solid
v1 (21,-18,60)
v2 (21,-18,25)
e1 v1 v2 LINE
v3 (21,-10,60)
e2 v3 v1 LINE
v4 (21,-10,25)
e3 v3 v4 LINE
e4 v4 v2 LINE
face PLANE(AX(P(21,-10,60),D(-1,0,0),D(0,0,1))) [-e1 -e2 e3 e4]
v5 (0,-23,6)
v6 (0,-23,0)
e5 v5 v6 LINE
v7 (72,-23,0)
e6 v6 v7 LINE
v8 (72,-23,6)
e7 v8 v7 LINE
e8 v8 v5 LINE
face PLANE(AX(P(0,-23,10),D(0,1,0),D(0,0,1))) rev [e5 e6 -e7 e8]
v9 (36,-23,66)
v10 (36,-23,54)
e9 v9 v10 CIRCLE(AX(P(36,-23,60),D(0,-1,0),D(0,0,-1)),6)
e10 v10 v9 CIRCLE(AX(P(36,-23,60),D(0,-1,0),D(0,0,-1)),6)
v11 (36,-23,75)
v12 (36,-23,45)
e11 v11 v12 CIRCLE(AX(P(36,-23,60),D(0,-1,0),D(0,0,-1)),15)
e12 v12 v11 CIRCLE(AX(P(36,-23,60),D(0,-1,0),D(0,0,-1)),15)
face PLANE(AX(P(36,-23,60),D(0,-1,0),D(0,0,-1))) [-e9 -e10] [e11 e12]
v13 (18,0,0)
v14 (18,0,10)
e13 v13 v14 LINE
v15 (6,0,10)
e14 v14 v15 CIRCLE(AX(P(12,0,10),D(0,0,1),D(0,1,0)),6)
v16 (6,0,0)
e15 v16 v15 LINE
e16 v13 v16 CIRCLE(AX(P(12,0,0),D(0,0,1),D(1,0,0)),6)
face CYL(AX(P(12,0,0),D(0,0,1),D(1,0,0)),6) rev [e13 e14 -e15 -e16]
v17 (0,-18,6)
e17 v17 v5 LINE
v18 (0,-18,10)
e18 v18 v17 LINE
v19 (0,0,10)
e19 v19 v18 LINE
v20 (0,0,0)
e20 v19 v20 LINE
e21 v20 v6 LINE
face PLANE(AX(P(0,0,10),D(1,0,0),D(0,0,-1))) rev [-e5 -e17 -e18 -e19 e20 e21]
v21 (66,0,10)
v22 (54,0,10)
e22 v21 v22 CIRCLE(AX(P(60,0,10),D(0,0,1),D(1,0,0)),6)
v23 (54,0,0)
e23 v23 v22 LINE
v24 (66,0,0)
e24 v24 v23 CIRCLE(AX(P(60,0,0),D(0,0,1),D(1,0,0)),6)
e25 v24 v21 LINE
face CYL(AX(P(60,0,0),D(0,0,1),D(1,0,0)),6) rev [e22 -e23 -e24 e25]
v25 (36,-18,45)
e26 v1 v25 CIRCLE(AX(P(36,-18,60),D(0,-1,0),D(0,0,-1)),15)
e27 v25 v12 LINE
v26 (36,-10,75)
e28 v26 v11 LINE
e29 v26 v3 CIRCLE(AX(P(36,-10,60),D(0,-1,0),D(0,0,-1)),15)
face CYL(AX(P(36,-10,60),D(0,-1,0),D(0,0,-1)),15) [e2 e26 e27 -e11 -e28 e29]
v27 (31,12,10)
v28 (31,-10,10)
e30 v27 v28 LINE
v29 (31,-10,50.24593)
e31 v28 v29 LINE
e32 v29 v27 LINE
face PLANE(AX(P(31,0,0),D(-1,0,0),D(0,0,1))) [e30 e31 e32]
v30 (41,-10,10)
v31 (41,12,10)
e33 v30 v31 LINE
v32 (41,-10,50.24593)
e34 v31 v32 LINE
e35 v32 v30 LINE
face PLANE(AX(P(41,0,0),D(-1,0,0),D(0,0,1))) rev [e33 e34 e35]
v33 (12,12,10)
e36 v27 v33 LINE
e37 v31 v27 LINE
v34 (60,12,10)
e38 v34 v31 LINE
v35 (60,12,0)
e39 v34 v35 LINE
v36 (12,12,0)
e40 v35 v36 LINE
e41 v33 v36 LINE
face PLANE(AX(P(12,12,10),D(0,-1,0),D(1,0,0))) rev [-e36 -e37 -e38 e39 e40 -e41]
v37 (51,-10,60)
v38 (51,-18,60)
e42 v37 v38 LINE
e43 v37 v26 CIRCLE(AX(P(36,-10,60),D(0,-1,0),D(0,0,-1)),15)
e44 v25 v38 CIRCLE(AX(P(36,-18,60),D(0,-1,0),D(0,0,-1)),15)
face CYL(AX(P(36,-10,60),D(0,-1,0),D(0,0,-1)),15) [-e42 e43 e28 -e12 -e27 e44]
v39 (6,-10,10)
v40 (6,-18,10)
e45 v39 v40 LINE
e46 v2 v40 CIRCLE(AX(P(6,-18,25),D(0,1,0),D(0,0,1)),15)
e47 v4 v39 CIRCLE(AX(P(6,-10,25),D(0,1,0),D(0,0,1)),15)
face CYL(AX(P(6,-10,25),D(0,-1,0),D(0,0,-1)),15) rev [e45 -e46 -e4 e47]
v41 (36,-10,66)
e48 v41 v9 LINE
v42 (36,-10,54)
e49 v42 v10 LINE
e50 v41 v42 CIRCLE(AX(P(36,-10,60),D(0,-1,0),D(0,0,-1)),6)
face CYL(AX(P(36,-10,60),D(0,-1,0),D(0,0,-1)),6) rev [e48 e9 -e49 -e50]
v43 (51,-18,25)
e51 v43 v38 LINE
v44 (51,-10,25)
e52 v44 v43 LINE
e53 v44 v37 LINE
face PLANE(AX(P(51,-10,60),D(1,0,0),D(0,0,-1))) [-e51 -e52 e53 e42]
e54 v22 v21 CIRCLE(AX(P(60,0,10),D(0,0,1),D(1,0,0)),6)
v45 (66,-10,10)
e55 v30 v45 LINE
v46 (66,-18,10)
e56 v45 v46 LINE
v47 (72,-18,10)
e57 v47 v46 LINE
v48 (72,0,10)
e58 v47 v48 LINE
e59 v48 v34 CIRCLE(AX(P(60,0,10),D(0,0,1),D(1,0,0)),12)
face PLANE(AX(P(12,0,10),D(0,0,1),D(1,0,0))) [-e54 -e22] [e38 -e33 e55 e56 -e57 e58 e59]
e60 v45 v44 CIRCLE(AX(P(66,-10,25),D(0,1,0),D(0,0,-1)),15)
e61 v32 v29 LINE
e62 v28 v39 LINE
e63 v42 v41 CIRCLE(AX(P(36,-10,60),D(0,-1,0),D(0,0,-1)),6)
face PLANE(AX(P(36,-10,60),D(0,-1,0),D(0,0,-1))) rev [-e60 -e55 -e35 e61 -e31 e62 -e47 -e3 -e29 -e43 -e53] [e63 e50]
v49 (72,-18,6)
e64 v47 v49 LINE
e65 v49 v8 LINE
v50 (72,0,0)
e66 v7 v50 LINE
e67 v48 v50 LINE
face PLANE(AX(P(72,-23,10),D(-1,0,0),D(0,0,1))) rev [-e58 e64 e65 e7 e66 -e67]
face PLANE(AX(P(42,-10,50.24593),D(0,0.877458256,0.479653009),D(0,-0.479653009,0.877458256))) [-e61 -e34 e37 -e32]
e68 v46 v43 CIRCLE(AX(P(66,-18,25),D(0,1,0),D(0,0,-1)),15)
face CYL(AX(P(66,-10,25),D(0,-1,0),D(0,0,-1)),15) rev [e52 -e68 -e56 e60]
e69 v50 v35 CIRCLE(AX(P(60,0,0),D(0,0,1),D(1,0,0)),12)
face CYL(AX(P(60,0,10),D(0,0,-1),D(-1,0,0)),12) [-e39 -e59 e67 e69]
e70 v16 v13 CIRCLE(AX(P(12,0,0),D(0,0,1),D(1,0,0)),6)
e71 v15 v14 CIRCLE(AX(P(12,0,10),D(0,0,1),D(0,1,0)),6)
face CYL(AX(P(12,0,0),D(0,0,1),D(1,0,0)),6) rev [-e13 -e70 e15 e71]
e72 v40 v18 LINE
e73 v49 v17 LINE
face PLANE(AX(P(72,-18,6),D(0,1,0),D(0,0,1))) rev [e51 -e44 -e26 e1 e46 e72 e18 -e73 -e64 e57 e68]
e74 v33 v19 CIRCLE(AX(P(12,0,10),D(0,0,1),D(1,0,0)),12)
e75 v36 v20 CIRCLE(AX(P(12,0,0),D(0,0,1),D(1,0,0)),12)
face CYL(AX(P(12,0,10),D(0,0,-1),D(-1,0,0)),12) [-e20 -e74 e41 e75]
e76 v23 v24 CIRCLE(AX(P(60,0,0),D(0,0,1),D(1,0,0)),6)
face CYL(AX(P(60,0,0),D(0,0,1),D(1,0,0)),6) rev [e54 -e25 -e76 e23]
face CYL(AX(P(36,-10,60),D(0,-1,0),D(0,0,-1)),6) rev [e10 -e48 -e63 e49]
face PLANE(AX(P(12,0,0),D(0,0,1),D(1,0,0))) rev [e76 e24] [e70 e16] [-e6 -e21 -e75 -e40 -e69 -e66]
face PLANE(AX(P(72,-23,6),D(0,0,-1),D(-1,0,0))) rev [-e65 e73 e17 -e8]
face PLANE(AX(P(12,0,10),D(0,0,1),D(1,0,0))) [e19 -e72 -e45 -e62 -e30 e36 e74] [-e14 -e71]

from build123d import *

# Parameters (mm, degrees)
MOUNTING_PLATE_DEPTH     = 10
PLATE_NOTCH_SKETCH_W     = 4
PLATE_NOTCH_SKETCH_H     = 5
PLATE_NOTCH_CUT_DEPTH    = 72
PIVOT_ARM_DEPTH          = 8
PIVOT_START              = 5
PIVOT_BOSS_SKETCH_R      = 15
PIVOT_BOSS_30_DEPTH      = 5
PLATE_HOLES_SKETCH_R     = 6
PLATE_HOLES_2X_12_DEPTH  = 10
PIVOT_HOLE_SKETCH_R      = 6
PIVOT_HOLE_12_DEPTH      = 13
GUSSET_BLANK_DEPTH       = 42
GUSSET_TAPER_CUT_DEPTH   = 30
GUSSET_EDGE_TRIM_A_DEPTH = 1
GUSSET_EDGE_TRIM_B_DEPTH = 1


with BuildPart() as part:
    # Plate Profile Sketch → Mounting Plate (new body)
    with BuildSketch(Plane.XY):
        with BuildLine():
            Line((0, 0), (0, -23))
            Line((0, -23), (72, -23))
            Line((72, -23), (72, 0))
            ThreePointArc((72, 0), (68.485281374, 8.485281374), (60, 12))
            Line((60, 12), (12, 12))
            ThreePointArc((12, 12), (3.514718626, 8.485281374), (0, 0))
        make_face()
    extrude(amount=MOUNTING_PLATE_DEPTH)

    # Plate Notch Sketch → Plate Notch Cut (cut)
    with BuildSketch(Plane.ZY):
        with Locations((8, -20.5)):
            Rectangle(PLATE_NOTCH_SKETCH_W, PLATE_NOTCH_SKETCH_H)
    extrude(amount=-PLATE_NOTCH_CUT_DEPTH, mode=Mode.SUBTRACT)

    # Arm Profile Sketch → Pivot Arm (add)
    with BuildSketch(Plane.XZ.offset(18)):
        with BuildLine():
            Line((6, 10), (66, 10))
            ThreePointArc((66, 10), (55.393398282, 14.393398282), (51, 25))
            Line((51, 25), (51, 60))
            ThreePointArc((51, 60), (36, 75), (21, 60))
            Line((21, 60), (21, 25))
            ThreePointArc((21, 25), (16.606601718, 14.393398282), (6, 10))
        make_face()
    extrude(amount=-PIVOT_ARM_DEPTH)

    # Pivot Boss Sketch → Pivot Boss Ø30 (add)
    with BuildSketch(Plane.XZ.offset(18).offset(PIVOT_START)):
        with Locations(Location((36, 60, 0), (0, 0, 270))):
            Circle(PIVOT_BOSS_SKETCH_R)
    extrude(amount=-PIVOT_BOSS_30_DEPTH)

    # Plate Holes Sketch → Plate Holes 2xØ12 (cut)
    with BuildSketch(Plane.XY.offset(10)):
        with Locations((12, 0)):
            Circle(PLATE_HOLES_SKETCH_R)
        with Locations((60, 0)):
            Circle(PLATE_HOLES_SKETCH_R)
    extrude(amount=-PLATE_HOLES_2X_12_DEPTH, mode=Mode.SUBTRACT)

    # Pivot Hole Sketch → Pivot Hole Ø12 (cut)
    with BuildSketch(Plane.XZ.offset(23)):
        with Locations(Location((36, 60, 0), (0, 0, 270))):
            Circle(PIVOT_HOLE_SKETCH_R)
    extrude(amount=-PIVOT_HOLE_12_DEPTH, mode=Mode.SUBTRACT)

    # Gusset Profile Sketch → Gusset Blank (add)
    with BuildSketch(Plane.ZY):
        Polygon((10, -10), (50.245930421, -10), (10, 12), align=None)
    extrude(amount=-GUSSET_BLANK_DEPTH)

    # Gusset Taper Sketch → Gusset Taper Cut (cut)
    with BuildSketch(Plane.ZY):
        Polygon((10, 12), (10, -10), (50.245930421, -10), align=None)
    extrude(amount=-GUSSET_TAPER_CUT_DEPTH, mode=Mode.SUBTRACT)

    # Gusset Edge Trim A Sketch → Gusset Edge Trim A (cut)
    with BuildSketch(Plane.ZY.offset(-30)):
        Polygon((10, 12), (10, -10), (50.245930421, -10), align=None)
    extrude(amount=-GUSSET_EDGE_TRIM_A_DEPTH, mode=Mode.SUBTRACT)

    # Gusset Edge Trim B Sketch → Gusset Edge Trim B (cut)
    with BuildSketch(Plane(origin=(42, 0, 0), x_dir=(0, 0, -1), z_dir=(1, 0, 0))):
        Polygon((-50.245930421, -10), (-10, -10), (-10, 12), align=None)
    extrude(amount=-GUSSET_EDGE_TRIM_B_DEPTH, mode=Mode.SUBTRACT)


solid = part.part
